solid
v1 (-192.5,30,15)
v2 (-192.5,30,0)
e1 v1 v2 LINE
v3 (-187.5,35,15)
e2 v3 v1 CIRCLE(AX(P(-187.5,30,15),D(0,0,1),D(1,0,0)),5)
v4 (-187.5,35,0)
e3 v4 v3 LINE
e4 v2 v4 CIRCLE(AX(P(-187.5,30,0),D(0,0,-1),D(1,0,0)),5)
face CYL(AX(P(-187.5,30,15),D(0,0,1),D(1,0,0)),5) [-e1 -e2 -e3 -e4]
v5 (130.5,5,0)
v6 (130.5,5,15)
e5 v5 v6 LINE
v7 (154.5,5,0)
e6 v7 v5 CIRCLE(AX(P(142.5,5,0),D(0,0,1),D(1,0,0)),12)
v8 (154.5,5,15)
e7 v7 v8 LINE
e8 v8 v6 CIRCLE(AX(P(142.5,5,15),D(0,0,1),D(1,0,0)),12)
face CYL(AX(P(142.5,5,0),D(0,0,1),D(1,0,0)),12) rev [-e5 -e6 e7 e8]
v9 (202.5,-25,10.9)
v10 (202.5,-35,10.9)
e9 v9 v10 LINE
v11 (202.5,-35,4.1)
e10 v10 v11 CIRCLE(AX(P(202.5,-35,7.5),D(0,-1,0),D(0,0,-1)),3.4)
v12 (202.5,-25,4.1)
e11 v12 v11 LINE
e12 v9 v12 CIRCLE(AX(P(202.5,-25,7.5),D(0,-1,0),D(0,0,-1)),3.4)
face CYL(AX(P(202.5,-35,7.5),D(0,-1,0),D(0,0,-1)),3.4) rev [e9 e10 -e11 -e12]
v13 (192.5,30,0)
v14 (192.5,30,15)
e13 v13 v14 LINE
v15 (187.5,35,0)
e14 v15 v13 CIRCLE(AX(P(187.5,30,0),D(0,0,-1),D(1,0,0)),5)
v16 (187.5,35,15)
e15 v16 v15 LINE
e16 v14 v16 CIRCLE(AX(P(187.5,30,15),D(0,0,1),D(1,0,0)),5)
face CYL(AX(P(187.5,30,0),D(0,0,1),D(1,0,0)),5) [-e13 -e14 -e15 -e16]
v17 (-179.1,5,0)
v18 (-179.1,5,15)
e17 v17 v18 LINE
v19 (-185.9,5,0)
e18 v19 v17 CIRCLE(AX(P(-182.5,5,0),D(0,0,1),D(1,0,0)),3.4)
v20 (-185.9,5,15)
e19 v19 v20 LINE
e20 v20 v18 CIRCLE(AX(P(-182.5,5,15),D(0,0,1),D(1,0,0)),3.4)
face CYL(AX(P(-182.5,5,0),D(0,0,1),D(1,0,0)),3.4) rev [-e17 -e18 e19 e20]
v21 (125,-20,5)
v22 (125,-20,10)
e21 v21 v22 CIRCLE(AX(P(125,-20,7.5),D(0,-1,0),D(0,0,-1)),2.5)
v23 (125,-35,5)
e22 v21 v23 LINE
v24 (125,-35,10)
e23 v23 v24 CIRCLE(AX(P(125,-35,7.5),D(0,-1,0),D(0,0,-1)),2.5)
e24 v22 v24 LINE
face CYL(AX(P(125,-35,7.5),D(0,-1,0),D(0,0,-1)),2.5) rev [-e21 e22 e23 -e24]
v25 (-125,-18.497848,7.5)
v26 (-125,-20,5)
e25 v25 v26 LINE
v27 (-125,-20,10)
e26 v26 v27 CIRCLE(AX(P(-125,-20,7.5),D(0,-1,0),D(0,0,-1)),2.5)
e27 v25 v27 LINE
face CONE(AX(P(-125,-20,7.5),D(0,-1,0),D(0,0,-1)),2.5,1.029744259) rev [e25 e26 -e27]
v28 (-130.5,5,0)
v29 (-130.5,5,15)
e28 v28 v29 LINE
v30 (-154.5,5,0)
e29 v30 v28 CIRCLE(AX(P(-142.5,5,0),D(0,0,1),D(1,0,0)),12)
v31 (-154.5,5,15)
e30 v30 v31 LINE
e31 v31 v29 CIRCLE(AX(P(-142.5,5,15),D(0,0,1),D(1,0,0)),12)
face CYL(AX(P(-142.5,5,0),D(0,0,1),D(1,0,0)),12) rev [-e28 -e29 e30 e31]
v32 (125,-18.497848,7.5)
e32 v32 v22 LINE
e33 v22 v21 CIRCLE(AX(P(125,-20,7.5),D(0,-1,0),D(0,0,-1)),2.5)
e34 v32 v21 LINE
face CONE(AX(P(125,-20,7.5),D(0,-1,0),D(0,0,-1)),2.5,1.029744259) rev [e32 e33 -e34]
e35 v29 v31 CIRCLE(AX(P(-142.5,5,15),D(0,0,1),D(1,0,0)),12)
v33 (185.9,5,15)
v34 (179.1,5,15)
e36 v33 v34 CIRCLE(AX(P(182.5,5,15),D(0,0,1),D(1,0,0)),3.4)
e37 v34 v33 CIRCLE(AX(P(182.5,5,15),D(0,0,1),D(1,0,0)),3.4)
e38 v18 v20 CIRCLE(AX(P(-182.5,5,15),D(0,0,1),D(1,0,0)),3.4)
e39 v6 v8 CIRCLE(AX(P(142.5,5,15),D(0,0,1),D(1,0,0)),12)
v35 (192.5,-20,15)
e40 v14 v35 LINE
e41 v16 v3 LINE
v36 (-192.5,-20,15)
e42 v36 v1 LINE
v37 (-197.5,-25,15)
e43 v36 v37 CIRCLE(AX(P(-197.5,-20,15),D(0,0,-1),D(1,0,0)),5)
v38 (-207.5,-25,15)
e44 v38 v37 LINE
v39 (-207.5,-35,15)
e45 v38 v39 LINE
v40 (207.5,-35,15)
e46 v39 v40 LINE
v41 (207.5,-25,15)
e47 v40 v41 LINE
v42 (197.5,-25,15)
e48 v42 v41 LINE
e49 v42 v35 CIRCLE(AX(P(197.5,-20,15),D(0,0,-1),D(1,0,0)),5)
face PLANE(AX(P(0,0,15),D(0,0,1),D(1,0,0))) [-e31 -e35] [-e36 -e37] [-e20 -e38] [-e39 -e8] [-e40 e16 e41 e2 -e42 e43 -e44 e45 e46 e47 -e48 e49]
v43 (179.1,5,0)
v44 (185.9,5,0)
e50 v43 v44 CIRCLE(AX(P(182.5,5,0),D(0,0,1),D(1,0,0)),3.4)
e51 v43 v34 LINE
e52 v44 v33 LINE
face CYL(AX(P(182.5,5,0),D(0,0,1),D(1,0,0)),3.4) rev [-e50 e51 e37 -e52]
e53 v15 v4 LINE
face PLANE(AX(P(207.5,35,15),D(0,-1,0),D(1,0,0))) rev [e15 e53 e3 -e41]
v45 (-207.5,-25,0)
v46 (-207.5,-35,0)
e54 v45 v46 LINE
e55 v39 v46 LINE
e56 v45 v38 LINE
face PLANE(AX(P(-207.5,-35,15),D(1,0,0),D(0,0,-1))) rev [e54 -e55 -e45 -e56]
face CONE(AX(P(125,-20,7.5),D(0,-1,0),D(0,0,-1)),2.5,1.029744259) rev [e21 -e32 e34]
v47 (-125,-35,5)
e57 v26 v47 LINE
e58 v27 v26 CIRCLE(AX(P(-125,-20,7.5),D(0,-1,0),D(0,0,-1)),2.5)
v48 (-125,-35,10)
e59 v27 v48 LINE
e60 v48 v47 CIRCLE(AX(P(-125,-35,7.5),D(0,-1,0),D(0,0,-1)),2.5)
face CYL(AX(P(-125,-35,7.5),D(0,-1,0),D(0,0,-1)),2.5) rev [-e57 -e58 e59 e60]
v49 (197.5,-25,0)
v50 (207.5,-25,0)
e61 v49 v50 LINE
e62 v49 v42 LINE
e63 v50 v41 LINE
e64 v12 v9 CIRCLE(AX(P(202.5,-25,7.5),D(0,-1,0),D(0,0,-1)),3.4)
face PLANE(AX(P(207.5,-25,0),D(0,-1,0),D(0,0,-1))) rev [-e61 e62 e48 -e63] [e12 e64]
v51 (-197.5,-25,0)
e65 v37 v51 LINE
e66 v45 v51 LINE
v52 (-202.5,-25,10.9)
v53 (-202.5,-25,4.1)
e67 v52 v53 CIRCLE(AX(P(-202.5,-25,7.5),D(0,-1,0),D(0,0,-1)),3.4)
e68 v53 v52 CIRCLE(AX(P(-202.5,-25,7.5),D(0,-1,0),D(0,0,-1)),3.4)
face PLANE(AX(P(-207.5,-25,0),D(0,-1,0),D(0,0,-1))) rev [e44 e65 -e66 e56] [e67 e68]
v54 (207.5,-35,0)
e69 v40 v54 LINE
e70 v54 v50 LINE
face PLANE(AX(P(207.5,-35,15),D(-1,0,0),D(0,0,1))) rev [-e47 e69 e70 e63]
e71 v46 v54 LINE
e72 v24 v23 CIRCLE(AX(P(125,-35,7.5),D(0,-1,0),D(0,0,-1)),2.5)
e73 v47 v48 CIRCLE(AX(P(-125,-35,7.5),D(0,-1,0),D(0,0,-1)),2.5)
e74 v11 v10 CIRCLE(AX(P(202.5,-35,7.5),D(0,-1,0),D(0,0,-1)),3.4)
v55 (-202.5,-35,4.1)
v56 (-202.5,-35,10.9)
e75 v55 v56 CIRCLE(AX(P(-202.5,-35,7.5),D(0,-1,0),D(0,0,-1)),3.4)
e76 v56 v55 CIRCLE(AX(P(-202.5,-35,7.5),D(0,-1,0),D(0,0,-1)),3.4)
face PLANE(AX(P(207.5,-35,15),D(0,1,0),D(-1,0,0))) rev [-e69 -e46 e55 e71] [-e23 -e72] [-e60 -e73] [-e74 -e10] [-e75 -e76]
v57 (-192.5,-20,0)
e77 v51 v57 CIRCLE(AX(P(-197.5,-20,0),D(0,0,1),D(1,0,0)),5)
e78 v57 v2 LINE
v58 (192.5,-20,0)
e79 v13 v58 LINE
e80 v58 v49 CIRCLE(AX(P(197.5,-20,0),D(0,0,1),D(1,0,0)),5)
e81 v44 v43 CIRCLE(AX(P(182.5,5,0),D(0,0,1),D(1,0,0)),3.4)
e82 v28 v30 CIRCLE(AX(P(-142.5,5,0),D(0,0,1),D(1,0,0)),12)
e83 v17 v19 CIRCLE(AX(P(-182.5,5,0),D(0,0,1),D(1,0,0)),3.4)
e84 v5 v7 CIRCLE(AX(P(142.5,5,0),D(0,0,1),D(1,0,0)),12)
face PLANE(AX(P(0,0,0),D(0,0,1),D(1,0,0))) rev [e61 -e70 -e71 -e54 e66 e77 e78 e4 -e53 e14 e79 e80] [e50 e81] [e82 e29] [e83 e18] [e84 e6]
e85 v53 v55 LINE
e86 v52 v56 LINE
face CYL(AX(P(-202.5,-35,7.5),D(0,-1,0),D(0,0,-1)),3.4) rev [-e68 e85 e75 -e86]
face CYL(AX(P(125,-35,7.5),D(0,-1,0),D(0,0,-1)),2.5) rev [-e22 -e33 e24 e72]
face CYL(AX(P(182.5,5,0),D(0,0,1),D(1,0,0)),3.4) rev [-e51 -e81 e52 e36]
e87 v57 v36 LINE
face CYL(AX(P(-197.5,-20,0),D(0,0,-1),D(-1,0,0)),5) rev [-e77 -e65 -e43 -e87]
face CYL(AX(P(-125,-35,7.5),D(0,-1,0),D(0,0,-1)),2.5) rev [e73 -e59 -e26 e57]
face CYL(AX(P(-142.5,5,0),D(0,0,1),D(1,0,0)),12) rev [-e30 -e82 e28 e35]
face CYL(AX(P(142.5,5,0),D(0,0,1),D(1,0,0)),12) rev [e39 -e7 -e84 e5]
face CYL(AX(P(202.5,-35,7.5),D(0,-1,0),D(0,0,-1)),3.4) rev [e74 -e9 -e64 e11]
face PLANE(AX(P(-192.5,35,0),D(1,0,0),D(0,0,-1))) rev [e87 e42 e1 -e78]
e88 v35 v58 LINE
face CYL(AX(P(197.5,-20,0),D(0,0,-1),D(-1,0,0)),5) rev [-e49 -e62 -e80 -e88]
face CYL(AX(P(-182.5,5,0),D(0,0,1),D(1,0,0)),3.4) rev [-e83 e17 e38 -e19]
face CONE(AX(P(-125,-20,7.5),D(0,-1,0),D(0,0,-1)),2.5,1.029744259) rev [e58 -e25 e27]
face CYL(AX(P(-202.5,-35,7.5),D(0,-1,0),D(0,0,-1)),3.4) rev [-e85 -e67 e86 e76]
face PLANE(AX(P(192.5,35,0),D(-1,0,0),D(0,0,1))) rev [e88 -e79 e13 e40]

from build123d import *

# Parameters (mm, degrees)
SKETCH1_W                      = 415
SKETCH1_H                      = 70
BOSS_EXTRUDE1_DEPTH            = 15
SKETCH2_R                      = 3.4
SKETCH2_R_2                    = 12
CUT_EXTRUDE1_DEPTH             = 211.965044498
SKETCH10_W                     = 15
SKETCH10_H                     = 60
CUT_EXTRUDE2_DEPTH             = 211.965044498
F_6_8_6_8_DIAMETER_HOLE1_D     = 6.8
F_6_8_6_8_DIAMETER_HOLE1_DEPTH = 12.4
F_6_8_6_8_DIAMETER_HOLE1_TIP   = 2.042926105
FILLET1_R                      = 5
FILLET2_R                      = 5
M6_TAPPED_HOLE1_D              = 5
M6_TAPPED_HOLE1_DEPTH          = 15
M6_TAPPED_HOLE1_TIP            = 1.502151548


with BuildPart() as part:
    # Sketch1 → Boss-Extrude1 (new body)
    with BuildSketch(Plane.XY):
        Rectangle(SKETCH1_W, SKETCH1_H)
    extrude(amount=BOSS_EXTRUDE1_DEPTH)

    # Sketch2 → Cut-Extrude1 (cut, through all)
    with BuildSketch(Plane.XY.offset(15)):
        with Locations((-182.5, 5)):
            Circle(SKETCH2_R)
        with Locations((-142.5, 5)):
            Circle(SKETCH2_R_2)
        with Locations((142.5, 5)):
            Circle(SKETCH2_R_2)
        with Locations((182.5, 5)):
            Circle(SKETCH2_R)
    extrude(amount=-CUT_EXTRUDE1_DEPTH, mode=Mode.SUBTRACT)

    # Sketch10 → Cut-Extrude2 (cut, through all)
    with BuildSketch(Plane.XY.offset(15)):
        with Locations((-200, 5)):
            Rectangle(SKETCH10_W, SKETCH10_H)
        with Locations((200, 5)):
            Rectangle(SKETCH10_W, SKETCH10_H)
    extrude(amount=-CUT_EXTRUDE2_DEPTH, mode=Mode.SUBTRACT)

    # Ø6.8 (6.8) Diameter Hole1
    with Locations(Plane(origin=(0, -35, 0), x_dir=(-1, 0, 0), z_dir=(0, -1, 0))):
        with Locations((-202.5, -7.5), (202.5, -7.5)):
            Hole(F_6_8_6_8_DIAMETER_HOLE1_D / 2, depth=F_6_8_6_8_DIAMETER_HOLE1_DEPTH)
            with Locations((0, 0, -(F_6_8_6_8_DIAMETER_HOLE1_DEPTH + F_6_8_6_8_DIAMETER_HOLE1_TIP / 2))):  # 118° drill point
                Cone(0, F_6_8_6_8_DIAMETER_HOLE1_D / 2, F_6_8_6_8_DIAMETER_HOLE1_TIP, mode=Mode.SUBTRACT)

    # Fillet1
    fillet1_edges = [part.edges().sort_by_distance(p)[0] for p in [
        (-192.5, -25, 7.5),
        (192.5, -25, 7.5),
    ]]
    fillet(fillet1_edges, radius=FILLET1_R)

    # Fillet2
    fillet2_edges = [part.edges().sort_by_distance(p)[0] for p in [
        (-192.5, 35, 7.5),
        (192.5, 35, 7.5),
    ]]
    fillet(fillet2_edges, radius=FILLET2_R)

    # M6 Tapped Hole1
    with Locations(Plane(origin=(0, -35, 0), x_dir=(-1, 0, 0), z_dir=(0, -1, 0))):
        with Locations((125, -7.5), (-125, -7.5)):
            Hole(M6_TAPPED_HOLE1_D / 2, depth=M6_TAPPED_HOLE1_DEPTH)
            with Locations((0, 0, -(M6_TAPPED_HOLE1_DEPTH + M6_TAPPED_HOLE1_TIP / 2))):  # 118° drill point
                Cone(0, M6_TAPPED_HOLE1_D / 2, M6_TAPPED_HOLE1_TIP, mode=Mode.SUBTRACT)


solid = part.part
